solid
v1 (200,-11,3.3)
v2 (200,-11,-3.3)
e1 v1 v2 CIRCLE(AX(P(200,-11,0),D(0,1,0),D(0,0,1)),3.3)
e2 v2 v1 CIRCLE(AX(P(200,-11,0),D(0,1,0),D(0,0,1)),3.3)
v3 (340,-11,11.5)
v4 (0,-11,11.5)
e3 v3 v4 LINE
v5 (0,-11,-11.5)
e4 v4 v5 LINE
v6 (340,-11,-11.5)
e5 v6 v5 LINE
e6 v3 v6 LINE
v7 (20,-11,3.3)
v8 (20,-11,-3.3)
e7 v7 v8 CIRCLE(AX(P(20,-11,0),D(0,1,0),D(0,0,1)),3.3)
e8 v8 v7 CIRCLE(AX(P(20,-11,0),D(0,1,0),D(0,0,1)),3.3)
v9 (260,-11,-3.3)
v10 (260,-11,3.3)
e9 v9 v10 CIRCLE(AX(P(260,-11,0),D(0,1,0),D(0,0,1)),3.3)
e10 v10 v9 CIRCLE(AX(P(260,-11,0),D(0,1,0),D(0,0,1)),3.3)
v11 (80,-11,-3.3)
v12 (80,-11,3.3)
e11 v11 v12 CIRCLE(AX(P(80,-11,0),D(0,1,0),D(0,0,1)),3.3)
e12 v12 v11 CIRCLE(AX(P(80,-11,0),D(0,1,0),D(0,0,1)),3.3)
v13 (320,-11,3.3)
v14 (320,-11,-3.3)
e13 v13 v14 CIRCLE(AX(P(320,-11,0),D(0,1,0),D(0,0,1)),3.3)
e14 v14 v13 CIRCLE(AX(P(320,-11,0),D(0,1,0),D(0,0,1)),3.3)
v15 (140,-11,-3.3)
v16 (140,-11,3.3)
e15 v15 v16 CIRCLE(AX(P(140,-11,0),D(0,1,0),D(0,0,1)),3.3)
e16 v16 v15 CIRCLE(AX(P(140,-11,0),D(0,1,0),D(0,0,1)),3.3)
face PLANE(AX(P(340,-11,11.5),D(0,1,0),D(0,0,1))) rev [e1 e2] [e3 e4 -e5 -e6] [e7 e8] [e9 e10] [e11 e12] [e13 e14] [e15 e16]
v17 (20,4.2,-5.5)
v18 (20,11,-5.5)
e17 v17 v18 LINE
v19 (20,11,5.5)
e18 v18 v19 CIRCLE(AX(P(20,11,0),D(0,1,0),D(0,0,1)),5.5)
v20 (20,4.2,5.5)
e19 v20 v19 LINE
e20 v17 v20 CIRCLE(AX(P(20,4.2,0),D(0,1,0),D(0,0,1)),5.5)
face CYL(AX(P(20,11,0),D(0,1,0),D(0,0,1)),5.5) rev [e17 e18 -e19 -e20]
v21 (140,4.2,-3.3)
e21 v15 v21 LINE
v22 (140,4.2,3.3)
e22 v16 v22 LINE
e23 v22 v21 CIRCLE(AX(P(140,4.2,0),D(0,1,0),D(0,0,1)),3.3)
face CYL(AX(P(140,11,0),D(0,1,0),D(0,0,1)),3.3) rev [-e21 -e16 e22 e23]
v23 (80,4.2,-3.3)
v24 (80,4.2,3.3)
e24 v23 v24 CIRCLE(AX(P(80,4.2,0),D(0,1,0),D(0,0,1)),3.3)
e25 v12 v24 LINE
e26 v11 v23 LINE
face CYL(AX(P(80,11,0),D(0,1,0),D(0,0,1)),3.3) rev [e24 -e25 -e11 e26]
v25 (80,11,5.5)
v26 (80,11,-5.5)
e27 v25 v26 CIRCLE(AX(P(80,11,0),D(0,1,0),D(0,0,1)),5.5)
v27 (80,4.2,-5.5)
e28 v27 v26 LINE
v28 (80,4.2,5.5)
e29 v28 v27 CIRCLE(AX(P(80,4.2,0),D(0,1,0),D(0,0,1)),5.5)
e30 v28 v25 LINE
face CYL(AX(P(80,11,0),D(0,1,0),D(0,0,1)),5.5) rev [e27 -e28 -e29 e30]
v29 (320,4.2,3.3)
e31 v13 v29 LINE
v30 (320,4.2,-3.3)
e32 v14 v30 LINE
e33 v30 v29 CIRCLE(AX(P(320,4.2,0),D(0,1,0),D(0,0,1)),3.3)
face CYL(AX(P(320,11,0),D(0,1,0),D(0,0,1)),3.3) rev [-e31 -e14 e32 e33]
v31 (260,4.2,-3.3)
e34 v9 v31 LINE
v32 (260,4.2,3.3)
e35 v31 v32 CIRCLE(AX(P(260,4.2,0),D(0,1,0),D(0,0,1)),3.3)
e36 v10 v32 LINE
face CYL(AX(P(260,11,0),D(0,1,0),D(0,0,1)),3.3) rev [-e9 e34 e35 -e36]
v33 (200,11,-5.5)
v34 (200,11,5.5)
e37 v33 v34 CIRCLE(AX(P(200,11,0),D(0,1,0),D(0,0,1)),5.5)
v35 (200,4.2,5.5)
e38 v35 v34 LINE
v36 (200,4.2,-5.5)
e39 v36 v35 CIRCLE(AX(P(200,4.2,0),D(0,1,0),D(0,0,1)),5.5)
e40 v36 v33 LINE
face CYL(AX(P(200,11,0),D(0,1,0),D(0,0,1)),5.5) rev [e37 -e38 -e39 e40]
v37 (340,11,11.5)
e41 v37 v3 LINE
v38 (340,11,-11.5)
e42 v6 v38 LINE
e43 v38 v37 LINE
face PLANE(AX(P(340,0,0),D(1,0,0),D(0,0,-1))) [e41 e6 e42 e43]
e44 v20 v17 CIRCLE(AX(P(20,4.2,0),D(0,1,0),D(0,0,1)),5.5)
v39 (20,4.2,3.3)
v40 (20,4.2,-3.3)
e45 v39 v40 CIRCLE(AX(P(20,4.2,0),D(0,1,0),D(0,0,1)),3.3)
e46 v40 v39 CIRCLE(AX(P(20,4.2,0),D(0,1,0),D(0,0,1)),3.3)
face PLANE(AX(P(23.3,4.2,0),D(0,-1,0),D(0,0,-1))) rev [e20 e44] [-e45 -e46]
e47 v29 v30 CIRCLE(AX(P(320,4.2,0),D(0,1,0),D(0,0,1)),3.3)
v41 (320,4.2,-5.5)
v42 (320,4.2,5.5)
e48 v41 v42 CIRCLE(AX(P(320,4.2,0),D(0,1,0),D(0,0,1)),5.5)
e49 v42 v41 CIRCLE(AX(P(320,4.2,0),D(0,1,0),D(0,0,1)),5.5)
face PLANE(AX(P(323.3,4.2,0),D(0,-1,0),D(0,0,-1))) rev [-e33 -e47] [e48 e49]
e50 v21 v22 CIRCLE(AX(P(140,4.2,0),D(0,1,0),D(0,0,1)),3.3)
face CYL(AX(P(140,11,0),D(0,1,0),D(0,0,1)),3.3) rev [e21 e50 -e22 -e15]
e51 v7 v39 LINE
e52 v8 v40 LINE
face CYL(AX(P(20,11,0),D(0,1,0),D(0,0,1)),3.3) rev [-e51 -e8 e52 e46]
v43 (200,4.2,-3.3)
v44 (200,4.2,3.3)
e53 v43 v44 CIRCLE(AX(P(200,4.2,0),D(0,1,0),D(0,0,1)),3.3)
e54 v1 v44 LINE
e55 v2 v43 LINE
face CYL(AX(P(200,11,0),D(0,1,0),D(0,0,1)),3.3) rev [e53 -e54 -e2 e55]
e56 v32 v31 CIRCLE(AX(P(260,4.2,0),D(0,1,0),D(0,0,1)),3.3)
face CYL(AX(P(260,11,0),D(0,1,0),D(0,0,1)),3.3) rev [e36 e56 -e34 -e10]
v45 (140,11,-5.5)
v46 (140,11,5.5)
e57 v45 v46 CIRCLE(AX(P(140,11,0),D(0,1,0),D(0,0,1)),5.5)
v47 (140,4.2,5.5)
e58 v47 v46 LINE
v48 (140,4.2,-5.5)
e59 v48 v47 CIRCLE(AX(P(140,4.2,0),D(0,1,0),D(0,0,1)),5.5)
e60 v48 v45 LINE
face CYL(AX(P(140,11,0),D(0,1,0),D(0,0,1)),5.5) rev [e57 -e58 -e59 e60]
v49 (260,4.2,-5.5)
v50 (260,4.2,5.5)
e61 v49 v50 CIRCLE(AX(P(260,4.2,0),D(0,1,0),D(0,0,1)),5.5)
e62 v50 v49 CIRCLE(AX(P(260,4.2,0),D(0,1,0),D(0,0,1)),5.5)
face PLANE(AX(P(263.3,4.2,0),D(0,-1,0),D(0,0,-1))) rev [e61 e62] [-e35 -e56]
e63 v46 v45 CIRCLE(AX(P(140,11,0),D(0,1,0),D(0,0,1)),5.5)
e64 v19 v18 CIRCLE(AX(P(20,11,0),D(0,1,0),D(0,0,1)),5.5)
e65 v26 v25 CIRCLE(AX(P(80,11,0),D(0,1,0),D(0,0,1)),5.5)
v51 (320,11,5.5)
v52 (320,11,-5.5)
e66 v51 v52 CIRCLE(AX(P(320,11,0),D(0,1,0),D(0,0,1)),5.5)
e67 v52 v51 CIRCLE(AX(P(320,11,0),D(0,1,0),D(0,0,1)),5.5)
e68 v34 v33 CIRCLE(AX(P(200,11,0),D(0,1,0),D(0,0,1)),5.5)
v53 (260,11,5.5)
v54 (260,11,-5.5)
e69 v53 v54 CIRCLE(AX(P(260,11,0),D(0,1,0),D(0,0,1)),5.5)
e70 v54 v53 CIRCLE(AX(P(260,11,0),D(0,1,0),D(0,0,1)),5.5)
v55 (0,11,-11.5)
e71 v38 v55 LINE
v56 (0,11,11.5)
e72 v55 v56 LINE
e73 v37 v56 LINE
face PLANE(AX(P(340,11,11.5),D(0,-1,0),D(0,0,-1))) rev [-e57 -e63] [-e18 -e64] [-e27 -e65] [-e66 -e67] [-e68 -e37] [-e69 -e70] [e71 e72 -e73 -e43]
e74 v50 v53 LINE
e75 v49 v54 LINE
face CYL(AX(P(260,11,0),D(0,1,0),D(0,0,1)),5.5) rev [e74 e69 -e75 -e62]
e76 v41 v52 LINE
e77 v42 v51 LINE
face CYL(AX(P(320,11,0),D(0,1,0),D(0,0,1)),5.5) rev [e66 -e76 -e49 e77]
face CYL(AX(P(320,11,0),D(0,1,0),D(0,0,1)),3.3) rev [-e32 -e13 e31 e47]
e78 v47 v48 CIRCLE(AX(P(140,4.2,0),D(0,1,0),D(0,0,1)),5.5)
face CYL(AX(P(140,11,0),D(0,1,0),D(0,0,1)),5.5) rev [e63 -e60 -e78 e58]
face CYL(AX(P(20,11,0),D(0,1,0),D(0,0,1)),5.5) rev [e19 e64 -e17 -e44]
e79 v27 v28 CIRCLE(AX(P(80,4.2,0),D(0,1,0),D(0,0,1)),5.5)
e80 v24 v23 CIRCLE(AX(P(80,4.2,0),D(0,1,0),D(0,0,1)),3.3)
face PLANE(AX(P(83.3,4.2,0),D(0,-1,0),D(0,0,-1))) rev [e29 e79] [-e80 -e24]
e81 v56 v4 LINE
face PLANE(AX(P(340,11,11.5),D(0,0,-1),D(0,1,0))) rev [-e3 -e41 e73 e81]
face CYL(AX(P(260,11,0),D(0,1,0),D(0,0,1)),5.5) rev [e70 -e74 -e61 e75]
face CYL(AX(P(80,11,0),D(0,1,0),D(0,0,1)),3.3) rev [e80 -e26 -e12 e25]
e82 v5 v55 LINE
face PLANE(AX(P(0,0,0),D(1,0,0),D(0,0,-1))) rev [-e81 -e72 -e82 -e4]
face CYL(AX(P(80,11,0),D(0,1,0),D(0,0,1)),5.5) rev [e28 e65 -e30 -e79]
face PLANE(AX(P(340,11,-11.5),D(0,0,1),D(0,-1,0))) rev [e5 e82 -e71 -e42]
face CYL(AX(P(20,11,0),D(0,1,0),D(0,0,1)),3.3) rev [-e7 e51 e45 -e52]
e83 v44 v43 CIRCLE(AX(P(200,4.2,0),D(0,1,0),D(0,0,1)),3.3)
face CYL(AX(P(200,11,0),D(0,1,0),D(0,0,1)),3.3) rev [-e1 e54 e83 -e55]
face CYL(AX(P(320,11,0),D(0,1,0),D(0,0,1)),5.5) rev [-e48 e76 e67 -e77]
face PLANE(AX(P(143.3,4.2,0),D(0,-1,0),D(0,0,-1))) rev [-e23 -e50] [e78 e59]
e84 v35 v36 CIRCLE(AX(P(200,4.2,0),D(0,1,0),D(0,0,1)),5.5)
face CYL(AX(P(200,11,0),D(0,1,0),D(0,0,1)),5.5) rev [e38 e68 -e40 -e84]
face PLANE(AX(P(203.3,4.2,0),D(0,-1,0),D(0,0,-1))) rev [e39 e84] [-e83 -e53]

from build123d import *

# Parameters (mm, degrees)
SKETCH_1_W                = 23
SKETCH_1_H                = 22
EXTRUDE_1_DEPTH           = 340
HOLE_WIZARD_1_D           = 6.6
HOLE_WIZARD_1_CBORE_D     = 11
HOLE_WIZARD_1_CBORE_DEPTH = 6.8
PATTERN_LINEAR_2_COUNT    = 6
PATTERN_LINEAR_2_PITCH    = 60


with BuildPart() as part:
    # 草图1 → 凸台-拉伸1 (new body)
    with BuildSketch(Plane(origin=(0, 0, 0), x_dir=(0, 0, -1), z_dir=(1, 0, 0))):
        Rectangle(SKETCH_1_W, SKETCH_1_H)
    extrude(amount=EXTRUDE_1_DEPTH)

    # 打孔尺寸(%根据)内六角圆柱头螺钉的类型1 (through all)
    with Locations(Plane(origin=(0, 11, 0), x_dir=(1, 0, 0), z_dir=(0, 1, 0))):
        with Locations((20, 0)):
            hole_wizard_1 = CounterBoreHole(HOLE_WIZARD_1_D / 2, HOLE_WIZARD_1_CBORE_D / 2, HOLE_WIZARD_1_CBORE_DEPTH)

    # 阵列(线性)2: 打孔尺寸(%根据)内六角圆柱头螺钉的类型1 ×6
    with Locations(*[(i * PATTERN_LINEAR_2_PITCH, 0, 0) for i in range(1, PATTERN_LINEAR_2_COUNT)]):
        add(hole_wizard_1, mode=Mode.SUBTRACT)


solid = part.part
